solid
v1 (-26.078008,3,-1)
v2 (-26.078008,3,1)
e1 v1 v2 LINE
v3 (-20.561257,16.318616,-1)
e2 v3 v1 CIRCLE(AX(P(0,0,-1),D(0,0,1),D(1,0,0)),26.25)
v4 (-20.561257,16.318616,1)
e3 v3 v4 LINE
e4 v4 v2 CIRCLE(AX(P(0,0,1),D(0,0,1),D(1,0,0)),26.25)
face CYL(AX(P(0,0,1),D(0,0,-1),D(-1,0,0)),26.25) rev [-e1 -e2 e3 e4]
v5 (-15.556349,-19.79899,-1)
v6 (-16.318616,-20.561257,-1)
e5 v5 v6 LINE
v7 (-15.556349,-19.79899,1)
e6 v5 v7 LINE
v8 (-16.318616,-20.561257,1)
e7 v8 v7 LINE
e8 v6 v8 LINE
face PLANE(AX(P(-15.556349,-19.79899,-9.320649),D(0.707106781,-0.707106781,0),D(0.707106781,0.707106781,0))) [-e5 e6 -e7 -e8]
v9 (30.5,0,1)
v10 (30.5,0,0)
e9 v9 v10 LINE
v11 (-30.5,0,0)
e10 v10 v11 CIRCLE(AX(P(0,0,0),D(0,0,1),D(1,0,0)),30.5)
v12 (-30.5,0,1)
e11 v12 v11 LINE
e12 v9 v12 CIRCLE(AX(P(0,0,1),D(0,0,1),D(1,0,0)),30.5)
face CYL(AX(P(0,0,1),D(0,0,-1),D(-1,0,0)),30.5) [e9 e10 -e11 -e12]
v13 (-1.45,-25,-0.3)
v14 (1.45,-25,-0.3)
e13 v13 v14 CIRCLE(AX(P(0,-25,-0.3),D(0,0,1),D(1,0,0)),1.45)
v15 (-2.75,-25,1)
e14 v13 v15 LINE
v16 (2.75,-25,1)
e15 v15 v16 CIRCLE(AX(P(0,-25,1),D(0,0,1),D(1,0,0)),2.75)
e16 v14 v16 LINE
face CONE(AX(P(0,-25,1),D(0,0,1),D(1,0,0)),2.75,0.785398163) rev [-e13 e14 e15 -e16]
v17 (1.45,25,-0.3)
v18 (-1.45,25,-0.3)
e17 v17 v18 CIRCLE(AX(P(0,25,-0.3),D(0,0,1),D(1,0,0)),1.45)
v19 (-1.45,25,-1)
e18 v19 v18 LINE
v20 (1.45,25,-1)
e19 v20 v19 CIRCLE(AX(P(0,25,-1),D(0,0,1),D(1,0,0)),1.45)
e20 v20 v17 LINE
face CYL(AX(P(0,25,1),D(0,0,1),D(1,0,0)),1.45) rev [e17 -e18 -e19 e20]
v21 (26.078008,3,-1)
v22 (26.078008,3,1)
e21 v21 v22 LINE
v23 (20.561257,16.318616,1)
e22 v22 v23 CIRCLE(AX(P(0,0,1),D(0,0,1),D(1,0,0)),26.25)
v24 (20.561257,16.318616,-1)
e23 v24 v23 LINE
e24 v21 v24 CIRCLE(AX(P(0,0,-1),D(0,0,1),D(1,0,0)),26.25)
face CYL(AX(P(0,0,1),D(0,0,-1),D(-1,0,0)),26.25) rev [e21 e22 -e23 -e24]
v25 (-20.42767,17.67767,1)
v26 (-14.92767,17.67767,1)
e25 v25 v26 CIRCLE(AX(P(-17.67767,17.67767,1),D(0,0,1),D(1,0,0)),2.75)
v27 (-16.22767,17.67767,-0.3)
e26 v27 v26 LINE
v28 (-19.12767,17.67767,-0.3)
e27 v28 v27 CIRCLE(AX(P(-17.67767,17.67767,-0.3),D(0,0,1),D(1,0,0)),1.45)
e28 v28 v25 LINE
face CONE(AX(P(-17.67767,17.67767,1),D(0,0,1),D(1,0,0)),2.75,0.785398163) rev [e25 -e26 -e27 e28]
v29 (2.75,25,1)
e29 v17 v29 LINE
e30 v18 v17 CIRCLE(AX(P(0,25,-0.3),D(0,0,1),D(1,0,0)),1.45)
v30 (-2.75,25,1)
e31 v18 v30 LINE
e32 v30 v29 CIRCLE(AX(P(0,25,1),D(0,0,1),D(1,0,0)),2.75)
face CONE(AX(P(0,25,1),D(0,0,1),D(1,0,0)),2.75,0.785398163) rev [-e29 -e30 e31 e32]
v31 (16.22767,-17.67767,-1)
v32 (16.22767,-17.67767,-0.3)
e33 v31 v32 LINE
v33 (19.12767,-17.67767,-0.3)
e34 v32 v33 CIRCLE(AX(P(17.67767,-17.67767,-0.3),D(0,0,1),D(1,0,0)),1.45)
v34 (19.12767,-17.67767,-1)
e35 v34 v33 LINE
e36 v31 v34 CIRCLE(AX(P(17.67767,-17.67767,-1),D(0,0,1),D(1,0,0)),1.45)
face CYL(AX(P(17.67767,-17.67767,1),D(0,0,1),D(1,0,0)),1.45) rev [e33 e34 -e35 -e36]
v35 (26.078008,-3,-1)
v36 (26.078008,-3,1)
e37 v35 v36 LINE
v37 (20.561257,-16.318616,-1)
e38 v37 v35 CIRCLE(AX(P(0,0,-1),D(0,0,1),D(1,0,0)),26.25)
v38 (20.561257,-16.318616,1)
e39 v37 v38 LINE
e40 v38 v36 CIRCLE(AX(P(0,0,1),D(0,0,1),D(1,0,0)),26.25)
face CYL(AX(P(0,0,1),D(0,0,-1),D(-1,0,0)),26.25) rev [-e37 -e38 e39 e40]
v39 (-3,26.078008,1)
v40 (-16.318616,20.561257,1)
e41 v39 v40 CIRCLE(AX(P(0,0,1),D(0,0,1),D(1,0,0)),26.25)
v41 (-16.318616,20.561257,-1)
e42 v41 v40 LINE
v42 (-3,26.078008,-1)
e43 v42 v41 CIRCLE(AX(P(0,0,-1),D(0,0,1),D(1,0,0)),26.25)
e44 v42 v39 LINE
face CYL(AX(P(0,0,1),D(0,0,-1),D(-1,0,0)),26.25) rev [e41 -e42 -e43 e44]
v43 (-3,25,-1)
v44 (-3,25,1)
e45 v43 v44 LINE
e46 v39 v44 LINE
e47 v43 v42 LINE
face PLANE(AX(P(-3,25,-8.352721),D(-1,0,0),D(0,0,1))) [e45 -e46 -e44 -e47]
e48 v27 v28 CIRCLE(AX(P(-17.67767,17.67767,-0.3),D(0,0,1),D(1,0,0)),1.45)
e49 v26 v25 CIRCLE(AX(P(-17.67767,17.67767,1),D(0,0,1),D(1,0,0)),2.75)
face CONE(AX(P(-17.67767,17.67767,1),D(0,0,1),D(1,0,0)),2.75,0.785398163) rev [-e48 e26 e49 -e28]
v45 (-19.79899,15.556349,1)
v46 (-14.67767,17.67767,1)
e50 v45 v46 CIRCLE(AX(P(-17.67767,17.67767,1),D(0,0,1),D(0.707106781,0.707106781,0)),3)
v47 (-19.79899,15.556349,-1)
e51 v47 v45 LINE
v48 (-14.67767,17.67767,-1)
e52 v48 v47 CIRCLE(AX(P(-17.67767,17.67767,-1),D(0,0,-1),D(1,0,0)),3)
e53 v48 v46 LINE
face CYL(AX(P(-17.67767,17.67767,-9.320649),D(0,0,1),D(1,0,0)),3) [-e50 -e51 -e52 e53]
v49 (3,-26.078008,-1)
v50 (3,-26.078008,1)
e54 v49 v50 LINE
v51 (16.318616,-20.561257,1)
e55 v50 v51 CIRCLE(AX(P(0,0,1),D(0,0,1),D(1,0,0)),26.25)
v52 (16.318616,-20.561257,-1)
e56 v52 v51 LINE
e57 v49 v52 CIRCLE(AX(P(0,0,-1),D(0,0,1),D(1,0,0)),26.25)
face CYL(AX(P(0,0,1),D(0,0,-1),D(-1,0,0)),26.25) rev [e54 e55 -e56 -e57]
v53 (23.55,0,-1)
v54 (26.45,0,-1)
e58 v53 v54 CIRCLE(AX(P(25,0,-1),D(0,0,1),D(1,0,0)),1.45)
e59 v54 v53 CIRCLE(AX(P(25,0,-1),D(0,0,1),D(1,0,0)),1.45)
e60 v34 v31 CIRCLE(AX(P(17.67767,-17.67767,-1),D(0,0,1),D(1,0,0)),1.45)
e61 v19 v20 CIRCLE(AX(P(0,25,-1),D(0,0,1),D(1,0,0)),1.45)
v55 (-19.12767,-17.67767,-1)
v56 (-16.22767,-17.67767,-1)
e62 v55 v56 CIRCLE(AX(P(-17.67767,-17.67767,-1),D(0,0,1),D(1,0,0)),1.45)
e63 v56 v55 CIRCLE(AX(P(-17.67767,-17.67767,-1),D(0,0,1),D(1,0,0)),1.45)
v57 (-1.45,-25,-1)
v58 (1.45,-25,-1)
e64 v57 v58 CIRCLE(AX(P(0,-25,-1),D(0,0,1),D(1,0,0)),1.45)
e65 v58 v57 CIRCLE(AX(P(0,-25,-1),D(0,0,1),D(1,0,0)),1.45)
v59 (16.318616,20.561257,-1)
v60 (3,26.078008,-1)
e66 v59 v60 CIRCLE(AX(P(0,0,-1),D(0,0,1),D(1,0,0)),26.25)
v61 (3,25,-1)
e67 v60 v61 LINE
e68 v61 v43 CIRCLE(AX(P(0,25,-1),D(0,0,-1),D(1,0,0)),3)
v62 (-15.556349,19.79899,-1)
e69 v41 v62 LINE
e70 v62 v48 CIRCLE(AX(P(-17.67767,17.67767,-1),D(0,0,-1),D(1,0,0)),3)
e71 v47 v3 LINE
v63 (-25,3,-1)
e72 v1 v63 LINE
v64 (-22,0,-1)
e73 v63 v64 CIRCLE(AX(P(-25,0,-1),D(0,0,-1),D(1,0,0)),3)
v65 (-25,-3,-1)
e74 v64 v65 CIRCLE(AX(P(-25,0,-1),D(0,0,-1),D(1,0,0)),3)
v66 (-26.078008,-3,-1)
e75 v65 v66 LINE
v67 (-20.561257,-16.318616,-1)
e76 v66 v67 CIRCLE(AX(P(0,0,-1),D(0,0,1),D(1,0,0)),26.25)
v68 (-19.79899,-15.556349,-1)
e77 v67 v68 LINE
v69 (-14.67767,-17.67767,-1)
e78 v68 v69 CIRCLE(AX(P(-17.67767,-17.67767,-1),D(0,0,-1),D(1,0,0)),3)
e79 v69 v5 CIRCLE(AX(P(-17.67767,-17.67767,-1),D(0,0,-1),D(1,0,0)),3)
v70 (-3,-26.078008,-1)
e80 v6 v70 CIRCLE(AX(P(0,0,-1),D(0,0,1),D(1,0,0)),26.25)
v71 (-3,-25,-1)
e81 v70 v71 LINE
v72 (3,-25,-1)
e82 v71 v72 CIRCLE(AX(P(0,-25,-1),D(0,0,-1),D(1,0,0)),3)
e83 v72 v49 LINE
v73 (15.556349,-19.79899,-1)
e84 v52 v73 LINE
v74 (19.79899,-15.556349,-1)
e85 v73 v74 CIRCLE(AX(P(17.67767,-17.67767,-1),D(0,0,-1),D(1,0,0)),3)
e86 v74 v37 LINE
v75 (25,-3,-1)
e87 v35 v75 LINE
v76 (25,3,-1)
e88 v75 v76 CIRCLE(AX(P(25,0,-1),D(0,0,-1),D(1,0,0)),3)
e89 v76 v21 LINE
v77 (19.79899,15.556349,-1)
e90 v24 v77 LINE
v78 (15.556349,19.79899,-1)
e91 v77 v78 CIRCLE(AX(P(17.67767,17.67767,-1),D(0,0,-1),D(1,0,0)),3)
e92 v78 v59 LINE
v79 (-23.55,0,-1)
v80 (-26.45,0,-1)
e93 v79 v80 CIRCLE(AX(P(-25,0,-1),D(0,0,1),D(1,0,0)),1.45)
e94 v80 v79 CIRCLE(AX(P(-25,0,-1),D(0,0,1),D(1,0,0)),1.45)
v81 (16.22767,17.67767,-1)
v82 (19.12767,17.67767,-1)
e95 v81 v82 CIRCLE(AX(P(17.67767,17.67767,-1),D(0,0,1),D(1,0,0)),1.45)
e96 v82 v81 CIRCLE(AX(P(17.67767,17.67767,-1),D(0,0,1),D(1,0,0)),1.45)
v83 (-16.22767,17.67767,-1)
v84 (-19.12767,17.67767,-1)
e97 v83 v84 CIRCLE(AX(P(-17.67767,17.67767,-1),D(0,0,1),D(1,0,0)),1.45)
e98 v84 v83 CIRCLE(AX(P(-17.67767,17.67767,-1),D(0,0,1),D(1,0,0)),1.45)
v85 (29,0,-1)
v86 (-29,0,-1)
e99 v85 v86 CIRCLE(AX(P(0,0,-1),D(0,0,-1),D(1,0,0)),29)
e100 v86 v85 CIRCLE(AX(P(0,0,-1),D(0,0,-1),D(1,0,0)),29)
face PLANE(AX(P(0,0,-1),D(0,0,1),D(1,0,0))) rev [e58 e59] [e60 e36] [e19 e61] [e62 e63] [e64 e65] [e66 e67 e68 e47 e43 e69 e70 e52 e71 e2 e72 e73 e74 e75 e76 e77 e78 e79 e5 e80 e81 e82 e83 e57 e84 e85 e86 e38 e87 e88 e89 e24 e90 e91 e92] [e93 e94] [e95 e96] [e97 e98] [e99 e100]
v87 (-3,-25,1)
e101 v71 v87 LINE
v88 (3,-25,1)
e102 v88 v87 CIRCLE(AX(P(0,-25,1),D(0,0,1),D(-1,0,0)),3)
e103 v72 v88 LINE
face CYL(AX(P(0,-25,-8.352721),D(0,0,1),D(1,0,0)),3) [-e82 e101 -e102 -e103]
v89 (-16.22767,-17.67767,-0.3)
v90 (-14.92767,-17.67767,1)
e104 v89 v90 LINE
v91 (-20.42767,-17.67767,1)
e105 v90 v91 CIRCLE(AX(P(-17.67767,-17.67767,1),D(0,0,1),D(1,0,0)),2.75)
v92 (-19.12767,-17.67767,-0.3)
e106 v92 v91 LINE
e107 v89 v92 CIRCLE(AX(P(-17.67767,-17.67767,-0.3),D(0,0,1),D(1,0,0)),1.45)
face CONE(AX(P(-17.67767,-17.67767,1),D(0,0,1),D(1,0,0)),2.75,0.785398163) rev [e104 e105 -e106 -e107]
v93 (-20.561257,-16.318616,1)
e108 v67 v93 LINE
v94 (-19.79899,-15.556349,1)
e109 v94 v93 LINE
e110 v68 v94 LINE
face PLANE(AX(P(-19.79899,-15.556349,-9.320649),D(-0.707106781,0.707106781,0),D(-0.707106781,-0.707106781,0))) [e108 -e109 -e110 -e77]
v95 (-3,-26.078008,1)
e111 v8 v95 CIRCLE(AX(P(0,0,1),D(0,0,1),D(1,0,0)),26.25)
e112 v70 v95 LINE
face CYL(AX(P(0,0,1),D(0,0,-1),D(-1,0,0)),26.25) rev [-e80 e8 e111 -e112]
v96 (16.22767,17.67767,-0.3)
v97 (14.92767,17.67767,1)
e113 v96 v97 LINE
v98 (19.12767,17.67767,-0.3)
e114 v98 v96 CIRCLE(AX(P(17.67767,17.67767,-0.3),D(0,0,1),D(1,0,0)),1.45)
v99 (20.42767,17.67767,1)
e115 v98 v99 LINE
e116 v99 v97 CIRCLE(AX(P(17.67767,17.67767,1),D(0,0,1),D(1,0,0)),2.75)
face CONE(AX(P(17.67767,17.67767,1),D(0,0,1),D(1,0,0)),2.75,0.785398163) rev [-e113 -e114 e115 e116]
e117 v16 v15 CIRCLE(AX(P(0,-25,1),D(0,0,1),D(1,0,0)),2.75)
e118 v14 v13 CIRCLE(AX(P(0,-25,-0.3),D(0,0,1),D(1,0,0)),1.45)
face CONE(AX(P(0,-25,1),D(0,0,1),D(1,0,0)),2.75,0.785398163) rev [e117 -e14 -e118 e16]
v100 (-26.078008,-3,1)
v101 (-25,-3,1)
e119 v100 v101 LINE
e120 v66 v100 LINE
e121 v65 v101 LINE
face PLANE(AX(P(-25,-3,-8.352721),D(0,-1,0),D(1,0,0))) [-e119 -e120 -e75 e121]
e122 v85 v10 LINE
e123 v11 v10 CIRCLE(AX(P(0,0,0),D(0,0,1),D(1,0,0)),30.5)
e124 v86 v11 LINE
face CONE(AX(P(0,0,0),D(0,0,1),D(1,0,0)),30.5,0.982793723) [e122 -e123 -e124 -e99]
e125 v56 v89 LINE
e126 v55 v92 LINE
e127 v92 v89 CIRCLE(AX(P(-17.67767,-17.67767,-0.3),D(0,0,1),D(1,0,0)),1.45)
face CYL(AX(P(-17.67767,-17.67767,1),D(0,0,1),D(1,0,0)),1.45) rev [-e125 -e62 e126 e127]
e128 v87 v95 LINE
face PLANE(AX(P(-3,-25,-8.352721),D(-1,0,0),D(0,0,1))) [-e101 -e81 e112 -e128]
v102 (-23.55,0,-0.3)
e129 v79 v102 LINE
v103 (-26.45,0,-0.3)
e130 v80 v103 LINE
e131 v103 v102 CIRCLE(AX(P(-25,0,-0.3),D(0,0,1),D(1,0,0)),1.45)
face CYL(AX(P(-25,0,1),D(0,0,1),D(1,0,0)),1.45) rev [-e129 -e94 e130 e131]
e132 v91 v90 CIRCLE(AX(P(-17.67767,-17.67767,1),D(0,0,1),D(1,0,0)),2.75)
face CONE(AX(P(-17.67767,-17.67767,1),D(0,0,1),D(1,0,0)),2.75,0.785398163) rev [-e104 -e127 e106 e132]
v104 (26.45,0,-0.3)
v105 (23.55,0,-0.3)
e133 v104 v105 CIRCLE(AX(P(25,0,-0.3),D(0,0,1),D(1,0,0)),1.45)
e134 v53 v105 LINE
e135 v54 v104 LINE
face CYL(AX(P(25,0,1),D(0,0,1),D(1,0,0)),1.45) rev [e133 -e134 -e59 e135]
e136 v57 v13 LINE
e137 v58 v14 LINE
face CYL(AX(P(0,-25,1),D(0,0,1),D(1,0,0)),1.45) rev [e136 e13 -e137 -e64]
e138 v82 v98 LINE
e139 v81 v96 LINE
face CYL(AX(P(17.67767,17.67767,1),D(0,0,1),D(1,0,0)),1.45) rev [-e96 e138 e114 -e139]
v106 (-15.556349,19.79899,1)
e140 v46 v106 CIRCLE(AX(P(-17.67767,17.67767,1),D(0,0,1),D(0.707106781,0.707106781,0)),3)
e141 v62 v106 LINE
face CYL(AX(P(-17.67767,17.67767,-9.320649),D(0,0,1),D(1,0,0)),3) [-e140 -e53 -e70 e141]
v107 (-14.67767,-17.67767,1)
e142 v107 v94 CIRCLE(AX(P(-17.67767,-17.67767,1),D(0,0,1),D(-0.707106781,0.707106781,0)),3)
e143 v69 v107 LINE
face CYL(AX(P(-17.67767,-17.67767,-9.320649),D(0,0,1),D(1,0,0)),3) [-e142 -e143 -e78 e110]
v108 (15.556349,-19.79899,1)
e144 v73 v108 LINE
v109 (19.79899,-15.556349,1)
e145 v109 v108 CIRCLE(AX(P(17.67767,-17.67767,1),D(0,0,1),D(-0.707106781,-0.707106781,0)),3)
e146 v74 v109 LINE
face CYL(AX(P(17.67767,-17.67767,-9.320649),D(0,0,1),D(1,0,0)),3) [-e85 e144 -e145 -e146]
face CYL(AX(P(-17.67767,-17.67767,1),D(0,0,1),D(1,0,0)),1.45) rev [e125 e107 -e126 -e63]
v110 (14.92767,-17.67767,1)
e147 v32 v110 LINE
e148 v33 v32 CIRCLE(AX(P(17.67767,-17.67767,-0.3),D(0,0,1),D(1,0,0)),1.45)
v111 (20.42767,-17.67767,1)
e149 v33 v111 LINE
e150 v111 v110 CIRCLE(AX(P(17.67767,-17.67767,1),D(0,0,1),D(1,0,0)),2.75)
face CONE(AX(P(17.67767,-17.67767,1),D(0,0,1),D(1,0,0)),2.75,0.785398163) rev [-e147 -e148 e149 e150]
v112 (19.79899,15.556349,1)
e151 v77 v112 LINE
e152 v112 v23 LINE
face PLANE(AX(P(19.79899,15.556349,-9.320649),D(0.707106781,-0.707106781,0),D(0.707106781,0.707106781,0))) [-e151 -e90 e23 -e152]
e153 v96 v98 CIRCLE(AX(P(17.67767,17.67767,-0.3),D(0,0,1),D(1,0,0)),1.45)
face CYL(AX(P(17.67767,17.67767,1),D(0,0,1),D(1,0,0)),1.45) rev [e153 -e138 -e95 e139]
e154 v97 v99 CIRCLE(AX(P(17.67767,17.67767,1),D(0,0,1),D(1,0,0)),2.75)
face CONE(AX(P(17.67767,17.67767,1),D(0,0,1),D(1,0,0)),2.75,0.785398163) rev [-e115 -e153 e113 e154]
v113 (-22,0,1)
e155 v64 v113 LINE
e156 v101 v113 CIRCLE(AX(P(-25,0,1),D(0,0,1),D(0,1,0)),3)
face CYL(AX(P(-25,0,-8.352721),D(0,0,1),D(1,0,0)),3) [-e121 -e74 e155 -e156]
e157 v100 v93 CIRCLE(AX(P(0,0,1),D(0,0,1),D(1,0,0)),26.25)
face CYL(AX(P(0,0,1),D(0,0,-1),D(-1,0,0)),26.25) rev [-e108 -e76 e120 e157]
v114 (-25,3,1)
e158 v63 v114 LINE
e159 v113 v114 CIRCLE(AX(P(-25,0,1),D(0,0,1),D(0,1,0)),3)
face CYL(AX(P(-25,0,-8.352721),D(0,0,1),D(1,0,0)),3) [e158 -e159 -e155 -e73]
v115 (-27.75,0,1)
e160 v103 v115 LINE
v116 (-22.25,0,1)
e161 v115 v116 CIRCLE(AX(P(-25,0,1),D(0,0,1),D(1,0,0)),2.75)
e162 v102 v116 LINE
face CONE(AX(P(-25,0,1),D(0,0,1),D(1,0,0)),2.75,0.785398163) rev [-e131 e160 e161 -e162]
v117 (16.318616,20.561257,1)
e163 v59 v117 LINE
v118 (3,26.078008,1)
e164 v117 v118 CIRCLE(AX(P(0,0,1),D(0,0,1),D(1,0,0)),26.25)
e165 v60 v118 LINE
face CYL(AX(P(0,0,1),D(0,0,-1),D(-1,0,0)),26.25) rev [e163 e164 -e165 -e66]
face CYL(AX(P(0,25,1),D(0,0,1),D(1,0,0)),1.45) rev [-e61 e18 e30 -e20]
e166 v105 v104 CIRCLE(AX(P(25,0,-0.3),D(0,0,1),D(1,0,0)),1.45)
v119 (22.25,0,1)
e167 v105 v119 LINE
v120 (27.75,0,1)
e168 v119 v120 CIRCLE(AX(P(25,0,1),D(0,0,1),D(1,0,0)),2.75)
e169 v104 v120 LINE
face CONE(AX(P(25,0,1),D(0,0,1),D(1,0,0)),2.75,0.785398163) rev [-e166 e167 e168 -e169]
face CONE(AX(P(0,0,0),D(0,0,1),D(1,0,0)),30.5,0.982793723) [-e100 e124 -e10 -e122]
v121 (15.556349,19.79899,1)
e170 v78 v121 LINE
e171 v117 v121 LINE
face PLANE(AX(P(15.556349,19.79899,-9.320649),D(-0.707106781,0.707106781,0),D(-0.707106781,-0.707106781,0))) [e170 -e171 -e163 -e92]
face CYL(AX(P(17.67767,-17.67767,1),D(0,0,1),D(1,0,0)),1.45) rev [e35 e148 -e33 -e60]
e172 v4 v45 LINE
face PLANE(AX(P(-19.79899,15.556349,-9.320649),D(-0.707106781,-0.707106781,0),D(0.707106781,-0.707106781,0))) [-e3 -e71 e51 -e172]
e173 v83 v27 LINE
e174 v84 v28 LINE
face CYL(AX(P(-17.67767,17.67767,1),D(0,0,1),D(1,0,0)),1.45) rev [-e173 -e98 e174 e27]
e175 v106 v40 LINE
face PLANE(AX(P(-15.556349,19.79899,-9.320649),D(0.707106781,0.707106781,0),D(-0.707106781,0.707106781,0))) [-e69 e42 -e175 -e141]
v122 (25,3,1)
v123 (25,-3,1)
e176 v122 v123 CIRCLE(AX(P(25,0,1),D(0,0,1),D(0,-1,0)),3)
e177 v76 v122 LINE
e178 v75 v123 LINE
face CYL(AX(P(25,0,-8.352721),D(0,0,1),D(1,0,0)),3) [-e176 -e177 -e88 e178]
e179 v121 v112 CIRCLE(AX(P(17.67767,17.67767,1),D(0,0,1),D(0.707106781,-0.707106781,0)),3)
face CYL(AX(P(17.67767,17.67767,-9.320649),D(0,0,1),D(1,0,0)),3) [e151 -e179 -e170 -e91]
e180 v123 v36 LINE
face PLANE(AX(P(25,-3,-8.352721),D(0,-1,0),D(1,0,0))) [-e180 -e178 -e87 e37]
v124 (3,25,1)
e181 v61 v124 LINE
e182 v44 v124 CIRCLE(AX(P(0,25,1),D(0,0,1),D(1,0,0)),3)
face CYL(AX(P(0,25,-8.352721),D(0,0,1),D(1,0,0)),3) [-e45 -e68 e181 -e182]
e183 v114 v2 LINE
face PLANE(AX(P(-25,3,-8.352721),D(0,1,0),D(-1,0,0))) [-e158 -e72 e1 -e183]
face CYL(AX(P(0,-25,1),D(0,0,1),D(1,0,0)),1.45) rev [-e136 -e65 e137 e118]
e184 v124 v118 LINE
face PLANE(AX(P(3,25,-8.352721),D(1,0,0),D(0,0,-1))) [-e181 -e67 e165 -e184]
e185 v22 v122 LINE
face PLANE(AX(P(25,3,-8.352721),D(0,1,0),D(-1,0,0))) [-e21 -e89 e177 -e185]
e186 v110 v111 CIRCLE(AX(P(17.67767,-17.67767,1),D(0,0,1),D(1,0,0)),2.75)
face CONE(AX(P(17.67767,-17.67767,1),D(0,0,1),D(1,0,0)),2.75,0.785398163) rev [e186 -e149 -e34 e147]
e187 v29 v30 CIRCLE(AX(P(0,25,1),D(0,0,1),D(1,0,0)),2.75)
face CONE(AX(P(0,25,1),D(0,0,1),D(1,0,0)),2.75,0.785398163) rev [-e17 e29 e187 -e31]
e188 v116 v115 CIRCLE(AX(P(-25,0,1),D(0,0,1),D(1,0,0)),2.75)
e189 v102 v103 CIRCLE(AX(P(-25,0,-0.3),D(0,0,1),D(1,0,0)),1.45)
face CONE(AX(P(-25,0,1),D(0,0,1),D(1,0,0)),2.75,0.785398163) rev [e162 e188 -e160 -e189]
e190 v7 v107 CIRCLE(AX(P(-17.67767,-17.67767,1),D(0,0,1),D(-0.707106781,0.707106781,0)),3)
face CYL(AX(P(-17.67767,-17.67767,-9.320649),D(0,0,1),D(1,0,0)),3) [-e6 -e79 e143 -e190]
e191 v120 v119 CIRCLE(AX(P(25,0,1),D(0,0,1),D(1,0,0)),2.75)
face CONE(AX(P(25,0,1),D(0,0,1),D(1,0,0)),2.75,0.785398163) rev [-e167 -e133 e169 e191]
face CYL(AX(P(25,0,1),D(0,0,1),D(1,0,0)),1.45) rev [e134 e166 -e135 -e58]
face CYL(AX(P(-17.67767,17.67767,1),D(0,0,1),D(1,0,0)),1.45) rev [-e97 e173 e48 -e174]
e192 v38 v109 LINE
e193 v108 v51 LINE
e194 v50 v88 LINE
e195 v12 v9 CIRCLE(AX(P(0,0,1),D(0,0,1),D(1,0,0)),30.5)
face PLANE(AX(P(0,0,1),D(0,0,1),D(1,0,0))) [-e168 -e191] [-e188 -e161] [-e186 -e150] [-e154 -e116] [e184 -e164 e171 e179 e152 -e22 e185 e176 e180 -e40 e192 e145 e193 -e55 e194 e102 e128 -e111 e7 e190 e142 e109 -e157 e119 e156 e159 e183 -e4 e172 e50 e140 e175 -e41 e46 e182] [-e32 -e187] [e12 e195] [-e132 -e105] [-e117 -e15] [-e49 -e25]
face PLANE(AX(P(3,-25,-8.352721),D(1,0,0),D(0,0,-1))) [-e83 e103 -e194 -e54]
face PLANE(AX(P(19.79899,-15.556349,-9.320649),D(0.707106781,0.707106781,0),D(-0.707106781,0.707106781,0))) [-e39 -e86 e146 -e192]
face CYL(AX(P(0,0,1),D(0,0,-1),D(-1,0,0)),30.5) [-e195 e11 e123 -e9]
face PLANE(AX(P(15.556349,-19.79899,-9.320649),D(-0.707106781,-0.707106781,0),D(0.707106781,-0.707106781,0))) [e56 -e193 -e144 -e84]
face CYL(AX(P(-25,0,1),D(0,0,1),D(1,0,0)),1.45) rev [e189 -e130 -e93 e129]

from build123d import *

# Parameters (mm, degrees)
SKETCH1_R           = 30.5
SKETCH1_R_2         = 26.25
BOSS_EXTRUDE1_DEPTH = 1
CHAMFER1_SIZE       = 1.5
CHAMFER1_SIZE2      = 1
BOSS_EXTRUDE2_START = -2
BOSS_EXTRUDE2_DEPTH = 2
CIRPATTERN2_COUNT   = 8


with BuildPart() as part:
    # Sketch1 → Boss-Extrude1 (new, symmetric)
    with BuildSketch(Plane.XY):
        Circle(SKETCH1_R)
        Circle(SKETCH1_R_2, mode=Mode.SUBTRACT)
    extrude(amount=BOSS_EXTRUDE1_DEPTH, both=True)

    # Chamfer1
    chamfer1_edges = [part.edges().sort_by_distance(p)[0] for p in [
        (-30.5, 0, -1),
    ]]
    chamfer1_side = [part.faces().sort_by_distance(p)[0] for p in [
        (-29.637329727, 0, -1),
    ]]
    chamfer(chamfer1_edges, length=CHAMFER1_SIZE, length2=CHAMFER1_SIZE2, reference=chamfer1_side[0])

    # Sketch4 → Boss-Extrude2 (add)
    with BuildSketch(Plane.XY.offset(1).offset(BOSS_EXTRUDE2_START)):
        with BuildLine():
            Line((-3, 25), (-3, 26.078007976))
            ThreePointArc((-3, 26.078007976), (0, 26.25), (3, 26.078007976))
            Line((3, 26.078007976), (3, 25))
            ThreePointArc((3, 25), (0, 22), (-3, 25))
        make_face()
    boss_extrude2 = extrude(amount=BOSS_EXTRUDE2_DEPTH)

    # Sketch5 → CSK for M2.5 Countersunk Flat Head Screw2 (revolve, cut)
    with BuildSketch(Plane(origin=(0, 25, 1), x_dir=(0, -1, 0), z_dir=(1, 0, 0))):
        Polygon((0, 0), (0, 2), (1.45, 2), (1.45, 1.3), (2.75, 0), align=None)
    csk_for_m2_5_countersunk_flat_head_screw = revolve(axis=Axis((0, 25, 7.35), (0, 0, -1)), mode=Mode.SUBTRACT)

    # CirPattern2: Boss-Extrude2, CSK for M2.5 Countersunk Flat Head Screw2 ×8 about axis
    cirpattern2_axis = Axis((0, 0, 0), (0, 0, 1))
    add([boss_extrude2.rotate(cirpattern2_axis, i * 360 / CIRPATTERN2_COUNT) for i in range(1, CIRPATTERN2_COUNT)])
    add([csk_for_m2_5_countersunk_flat_head_screw.rotate(cirpattern2_axis, i * 360 / CIRPATTERN2_COUNT) for i in range(1, CIRPATTERN2_COUNT)], mode=Mode.SUBTRACT)


solid = part.part
